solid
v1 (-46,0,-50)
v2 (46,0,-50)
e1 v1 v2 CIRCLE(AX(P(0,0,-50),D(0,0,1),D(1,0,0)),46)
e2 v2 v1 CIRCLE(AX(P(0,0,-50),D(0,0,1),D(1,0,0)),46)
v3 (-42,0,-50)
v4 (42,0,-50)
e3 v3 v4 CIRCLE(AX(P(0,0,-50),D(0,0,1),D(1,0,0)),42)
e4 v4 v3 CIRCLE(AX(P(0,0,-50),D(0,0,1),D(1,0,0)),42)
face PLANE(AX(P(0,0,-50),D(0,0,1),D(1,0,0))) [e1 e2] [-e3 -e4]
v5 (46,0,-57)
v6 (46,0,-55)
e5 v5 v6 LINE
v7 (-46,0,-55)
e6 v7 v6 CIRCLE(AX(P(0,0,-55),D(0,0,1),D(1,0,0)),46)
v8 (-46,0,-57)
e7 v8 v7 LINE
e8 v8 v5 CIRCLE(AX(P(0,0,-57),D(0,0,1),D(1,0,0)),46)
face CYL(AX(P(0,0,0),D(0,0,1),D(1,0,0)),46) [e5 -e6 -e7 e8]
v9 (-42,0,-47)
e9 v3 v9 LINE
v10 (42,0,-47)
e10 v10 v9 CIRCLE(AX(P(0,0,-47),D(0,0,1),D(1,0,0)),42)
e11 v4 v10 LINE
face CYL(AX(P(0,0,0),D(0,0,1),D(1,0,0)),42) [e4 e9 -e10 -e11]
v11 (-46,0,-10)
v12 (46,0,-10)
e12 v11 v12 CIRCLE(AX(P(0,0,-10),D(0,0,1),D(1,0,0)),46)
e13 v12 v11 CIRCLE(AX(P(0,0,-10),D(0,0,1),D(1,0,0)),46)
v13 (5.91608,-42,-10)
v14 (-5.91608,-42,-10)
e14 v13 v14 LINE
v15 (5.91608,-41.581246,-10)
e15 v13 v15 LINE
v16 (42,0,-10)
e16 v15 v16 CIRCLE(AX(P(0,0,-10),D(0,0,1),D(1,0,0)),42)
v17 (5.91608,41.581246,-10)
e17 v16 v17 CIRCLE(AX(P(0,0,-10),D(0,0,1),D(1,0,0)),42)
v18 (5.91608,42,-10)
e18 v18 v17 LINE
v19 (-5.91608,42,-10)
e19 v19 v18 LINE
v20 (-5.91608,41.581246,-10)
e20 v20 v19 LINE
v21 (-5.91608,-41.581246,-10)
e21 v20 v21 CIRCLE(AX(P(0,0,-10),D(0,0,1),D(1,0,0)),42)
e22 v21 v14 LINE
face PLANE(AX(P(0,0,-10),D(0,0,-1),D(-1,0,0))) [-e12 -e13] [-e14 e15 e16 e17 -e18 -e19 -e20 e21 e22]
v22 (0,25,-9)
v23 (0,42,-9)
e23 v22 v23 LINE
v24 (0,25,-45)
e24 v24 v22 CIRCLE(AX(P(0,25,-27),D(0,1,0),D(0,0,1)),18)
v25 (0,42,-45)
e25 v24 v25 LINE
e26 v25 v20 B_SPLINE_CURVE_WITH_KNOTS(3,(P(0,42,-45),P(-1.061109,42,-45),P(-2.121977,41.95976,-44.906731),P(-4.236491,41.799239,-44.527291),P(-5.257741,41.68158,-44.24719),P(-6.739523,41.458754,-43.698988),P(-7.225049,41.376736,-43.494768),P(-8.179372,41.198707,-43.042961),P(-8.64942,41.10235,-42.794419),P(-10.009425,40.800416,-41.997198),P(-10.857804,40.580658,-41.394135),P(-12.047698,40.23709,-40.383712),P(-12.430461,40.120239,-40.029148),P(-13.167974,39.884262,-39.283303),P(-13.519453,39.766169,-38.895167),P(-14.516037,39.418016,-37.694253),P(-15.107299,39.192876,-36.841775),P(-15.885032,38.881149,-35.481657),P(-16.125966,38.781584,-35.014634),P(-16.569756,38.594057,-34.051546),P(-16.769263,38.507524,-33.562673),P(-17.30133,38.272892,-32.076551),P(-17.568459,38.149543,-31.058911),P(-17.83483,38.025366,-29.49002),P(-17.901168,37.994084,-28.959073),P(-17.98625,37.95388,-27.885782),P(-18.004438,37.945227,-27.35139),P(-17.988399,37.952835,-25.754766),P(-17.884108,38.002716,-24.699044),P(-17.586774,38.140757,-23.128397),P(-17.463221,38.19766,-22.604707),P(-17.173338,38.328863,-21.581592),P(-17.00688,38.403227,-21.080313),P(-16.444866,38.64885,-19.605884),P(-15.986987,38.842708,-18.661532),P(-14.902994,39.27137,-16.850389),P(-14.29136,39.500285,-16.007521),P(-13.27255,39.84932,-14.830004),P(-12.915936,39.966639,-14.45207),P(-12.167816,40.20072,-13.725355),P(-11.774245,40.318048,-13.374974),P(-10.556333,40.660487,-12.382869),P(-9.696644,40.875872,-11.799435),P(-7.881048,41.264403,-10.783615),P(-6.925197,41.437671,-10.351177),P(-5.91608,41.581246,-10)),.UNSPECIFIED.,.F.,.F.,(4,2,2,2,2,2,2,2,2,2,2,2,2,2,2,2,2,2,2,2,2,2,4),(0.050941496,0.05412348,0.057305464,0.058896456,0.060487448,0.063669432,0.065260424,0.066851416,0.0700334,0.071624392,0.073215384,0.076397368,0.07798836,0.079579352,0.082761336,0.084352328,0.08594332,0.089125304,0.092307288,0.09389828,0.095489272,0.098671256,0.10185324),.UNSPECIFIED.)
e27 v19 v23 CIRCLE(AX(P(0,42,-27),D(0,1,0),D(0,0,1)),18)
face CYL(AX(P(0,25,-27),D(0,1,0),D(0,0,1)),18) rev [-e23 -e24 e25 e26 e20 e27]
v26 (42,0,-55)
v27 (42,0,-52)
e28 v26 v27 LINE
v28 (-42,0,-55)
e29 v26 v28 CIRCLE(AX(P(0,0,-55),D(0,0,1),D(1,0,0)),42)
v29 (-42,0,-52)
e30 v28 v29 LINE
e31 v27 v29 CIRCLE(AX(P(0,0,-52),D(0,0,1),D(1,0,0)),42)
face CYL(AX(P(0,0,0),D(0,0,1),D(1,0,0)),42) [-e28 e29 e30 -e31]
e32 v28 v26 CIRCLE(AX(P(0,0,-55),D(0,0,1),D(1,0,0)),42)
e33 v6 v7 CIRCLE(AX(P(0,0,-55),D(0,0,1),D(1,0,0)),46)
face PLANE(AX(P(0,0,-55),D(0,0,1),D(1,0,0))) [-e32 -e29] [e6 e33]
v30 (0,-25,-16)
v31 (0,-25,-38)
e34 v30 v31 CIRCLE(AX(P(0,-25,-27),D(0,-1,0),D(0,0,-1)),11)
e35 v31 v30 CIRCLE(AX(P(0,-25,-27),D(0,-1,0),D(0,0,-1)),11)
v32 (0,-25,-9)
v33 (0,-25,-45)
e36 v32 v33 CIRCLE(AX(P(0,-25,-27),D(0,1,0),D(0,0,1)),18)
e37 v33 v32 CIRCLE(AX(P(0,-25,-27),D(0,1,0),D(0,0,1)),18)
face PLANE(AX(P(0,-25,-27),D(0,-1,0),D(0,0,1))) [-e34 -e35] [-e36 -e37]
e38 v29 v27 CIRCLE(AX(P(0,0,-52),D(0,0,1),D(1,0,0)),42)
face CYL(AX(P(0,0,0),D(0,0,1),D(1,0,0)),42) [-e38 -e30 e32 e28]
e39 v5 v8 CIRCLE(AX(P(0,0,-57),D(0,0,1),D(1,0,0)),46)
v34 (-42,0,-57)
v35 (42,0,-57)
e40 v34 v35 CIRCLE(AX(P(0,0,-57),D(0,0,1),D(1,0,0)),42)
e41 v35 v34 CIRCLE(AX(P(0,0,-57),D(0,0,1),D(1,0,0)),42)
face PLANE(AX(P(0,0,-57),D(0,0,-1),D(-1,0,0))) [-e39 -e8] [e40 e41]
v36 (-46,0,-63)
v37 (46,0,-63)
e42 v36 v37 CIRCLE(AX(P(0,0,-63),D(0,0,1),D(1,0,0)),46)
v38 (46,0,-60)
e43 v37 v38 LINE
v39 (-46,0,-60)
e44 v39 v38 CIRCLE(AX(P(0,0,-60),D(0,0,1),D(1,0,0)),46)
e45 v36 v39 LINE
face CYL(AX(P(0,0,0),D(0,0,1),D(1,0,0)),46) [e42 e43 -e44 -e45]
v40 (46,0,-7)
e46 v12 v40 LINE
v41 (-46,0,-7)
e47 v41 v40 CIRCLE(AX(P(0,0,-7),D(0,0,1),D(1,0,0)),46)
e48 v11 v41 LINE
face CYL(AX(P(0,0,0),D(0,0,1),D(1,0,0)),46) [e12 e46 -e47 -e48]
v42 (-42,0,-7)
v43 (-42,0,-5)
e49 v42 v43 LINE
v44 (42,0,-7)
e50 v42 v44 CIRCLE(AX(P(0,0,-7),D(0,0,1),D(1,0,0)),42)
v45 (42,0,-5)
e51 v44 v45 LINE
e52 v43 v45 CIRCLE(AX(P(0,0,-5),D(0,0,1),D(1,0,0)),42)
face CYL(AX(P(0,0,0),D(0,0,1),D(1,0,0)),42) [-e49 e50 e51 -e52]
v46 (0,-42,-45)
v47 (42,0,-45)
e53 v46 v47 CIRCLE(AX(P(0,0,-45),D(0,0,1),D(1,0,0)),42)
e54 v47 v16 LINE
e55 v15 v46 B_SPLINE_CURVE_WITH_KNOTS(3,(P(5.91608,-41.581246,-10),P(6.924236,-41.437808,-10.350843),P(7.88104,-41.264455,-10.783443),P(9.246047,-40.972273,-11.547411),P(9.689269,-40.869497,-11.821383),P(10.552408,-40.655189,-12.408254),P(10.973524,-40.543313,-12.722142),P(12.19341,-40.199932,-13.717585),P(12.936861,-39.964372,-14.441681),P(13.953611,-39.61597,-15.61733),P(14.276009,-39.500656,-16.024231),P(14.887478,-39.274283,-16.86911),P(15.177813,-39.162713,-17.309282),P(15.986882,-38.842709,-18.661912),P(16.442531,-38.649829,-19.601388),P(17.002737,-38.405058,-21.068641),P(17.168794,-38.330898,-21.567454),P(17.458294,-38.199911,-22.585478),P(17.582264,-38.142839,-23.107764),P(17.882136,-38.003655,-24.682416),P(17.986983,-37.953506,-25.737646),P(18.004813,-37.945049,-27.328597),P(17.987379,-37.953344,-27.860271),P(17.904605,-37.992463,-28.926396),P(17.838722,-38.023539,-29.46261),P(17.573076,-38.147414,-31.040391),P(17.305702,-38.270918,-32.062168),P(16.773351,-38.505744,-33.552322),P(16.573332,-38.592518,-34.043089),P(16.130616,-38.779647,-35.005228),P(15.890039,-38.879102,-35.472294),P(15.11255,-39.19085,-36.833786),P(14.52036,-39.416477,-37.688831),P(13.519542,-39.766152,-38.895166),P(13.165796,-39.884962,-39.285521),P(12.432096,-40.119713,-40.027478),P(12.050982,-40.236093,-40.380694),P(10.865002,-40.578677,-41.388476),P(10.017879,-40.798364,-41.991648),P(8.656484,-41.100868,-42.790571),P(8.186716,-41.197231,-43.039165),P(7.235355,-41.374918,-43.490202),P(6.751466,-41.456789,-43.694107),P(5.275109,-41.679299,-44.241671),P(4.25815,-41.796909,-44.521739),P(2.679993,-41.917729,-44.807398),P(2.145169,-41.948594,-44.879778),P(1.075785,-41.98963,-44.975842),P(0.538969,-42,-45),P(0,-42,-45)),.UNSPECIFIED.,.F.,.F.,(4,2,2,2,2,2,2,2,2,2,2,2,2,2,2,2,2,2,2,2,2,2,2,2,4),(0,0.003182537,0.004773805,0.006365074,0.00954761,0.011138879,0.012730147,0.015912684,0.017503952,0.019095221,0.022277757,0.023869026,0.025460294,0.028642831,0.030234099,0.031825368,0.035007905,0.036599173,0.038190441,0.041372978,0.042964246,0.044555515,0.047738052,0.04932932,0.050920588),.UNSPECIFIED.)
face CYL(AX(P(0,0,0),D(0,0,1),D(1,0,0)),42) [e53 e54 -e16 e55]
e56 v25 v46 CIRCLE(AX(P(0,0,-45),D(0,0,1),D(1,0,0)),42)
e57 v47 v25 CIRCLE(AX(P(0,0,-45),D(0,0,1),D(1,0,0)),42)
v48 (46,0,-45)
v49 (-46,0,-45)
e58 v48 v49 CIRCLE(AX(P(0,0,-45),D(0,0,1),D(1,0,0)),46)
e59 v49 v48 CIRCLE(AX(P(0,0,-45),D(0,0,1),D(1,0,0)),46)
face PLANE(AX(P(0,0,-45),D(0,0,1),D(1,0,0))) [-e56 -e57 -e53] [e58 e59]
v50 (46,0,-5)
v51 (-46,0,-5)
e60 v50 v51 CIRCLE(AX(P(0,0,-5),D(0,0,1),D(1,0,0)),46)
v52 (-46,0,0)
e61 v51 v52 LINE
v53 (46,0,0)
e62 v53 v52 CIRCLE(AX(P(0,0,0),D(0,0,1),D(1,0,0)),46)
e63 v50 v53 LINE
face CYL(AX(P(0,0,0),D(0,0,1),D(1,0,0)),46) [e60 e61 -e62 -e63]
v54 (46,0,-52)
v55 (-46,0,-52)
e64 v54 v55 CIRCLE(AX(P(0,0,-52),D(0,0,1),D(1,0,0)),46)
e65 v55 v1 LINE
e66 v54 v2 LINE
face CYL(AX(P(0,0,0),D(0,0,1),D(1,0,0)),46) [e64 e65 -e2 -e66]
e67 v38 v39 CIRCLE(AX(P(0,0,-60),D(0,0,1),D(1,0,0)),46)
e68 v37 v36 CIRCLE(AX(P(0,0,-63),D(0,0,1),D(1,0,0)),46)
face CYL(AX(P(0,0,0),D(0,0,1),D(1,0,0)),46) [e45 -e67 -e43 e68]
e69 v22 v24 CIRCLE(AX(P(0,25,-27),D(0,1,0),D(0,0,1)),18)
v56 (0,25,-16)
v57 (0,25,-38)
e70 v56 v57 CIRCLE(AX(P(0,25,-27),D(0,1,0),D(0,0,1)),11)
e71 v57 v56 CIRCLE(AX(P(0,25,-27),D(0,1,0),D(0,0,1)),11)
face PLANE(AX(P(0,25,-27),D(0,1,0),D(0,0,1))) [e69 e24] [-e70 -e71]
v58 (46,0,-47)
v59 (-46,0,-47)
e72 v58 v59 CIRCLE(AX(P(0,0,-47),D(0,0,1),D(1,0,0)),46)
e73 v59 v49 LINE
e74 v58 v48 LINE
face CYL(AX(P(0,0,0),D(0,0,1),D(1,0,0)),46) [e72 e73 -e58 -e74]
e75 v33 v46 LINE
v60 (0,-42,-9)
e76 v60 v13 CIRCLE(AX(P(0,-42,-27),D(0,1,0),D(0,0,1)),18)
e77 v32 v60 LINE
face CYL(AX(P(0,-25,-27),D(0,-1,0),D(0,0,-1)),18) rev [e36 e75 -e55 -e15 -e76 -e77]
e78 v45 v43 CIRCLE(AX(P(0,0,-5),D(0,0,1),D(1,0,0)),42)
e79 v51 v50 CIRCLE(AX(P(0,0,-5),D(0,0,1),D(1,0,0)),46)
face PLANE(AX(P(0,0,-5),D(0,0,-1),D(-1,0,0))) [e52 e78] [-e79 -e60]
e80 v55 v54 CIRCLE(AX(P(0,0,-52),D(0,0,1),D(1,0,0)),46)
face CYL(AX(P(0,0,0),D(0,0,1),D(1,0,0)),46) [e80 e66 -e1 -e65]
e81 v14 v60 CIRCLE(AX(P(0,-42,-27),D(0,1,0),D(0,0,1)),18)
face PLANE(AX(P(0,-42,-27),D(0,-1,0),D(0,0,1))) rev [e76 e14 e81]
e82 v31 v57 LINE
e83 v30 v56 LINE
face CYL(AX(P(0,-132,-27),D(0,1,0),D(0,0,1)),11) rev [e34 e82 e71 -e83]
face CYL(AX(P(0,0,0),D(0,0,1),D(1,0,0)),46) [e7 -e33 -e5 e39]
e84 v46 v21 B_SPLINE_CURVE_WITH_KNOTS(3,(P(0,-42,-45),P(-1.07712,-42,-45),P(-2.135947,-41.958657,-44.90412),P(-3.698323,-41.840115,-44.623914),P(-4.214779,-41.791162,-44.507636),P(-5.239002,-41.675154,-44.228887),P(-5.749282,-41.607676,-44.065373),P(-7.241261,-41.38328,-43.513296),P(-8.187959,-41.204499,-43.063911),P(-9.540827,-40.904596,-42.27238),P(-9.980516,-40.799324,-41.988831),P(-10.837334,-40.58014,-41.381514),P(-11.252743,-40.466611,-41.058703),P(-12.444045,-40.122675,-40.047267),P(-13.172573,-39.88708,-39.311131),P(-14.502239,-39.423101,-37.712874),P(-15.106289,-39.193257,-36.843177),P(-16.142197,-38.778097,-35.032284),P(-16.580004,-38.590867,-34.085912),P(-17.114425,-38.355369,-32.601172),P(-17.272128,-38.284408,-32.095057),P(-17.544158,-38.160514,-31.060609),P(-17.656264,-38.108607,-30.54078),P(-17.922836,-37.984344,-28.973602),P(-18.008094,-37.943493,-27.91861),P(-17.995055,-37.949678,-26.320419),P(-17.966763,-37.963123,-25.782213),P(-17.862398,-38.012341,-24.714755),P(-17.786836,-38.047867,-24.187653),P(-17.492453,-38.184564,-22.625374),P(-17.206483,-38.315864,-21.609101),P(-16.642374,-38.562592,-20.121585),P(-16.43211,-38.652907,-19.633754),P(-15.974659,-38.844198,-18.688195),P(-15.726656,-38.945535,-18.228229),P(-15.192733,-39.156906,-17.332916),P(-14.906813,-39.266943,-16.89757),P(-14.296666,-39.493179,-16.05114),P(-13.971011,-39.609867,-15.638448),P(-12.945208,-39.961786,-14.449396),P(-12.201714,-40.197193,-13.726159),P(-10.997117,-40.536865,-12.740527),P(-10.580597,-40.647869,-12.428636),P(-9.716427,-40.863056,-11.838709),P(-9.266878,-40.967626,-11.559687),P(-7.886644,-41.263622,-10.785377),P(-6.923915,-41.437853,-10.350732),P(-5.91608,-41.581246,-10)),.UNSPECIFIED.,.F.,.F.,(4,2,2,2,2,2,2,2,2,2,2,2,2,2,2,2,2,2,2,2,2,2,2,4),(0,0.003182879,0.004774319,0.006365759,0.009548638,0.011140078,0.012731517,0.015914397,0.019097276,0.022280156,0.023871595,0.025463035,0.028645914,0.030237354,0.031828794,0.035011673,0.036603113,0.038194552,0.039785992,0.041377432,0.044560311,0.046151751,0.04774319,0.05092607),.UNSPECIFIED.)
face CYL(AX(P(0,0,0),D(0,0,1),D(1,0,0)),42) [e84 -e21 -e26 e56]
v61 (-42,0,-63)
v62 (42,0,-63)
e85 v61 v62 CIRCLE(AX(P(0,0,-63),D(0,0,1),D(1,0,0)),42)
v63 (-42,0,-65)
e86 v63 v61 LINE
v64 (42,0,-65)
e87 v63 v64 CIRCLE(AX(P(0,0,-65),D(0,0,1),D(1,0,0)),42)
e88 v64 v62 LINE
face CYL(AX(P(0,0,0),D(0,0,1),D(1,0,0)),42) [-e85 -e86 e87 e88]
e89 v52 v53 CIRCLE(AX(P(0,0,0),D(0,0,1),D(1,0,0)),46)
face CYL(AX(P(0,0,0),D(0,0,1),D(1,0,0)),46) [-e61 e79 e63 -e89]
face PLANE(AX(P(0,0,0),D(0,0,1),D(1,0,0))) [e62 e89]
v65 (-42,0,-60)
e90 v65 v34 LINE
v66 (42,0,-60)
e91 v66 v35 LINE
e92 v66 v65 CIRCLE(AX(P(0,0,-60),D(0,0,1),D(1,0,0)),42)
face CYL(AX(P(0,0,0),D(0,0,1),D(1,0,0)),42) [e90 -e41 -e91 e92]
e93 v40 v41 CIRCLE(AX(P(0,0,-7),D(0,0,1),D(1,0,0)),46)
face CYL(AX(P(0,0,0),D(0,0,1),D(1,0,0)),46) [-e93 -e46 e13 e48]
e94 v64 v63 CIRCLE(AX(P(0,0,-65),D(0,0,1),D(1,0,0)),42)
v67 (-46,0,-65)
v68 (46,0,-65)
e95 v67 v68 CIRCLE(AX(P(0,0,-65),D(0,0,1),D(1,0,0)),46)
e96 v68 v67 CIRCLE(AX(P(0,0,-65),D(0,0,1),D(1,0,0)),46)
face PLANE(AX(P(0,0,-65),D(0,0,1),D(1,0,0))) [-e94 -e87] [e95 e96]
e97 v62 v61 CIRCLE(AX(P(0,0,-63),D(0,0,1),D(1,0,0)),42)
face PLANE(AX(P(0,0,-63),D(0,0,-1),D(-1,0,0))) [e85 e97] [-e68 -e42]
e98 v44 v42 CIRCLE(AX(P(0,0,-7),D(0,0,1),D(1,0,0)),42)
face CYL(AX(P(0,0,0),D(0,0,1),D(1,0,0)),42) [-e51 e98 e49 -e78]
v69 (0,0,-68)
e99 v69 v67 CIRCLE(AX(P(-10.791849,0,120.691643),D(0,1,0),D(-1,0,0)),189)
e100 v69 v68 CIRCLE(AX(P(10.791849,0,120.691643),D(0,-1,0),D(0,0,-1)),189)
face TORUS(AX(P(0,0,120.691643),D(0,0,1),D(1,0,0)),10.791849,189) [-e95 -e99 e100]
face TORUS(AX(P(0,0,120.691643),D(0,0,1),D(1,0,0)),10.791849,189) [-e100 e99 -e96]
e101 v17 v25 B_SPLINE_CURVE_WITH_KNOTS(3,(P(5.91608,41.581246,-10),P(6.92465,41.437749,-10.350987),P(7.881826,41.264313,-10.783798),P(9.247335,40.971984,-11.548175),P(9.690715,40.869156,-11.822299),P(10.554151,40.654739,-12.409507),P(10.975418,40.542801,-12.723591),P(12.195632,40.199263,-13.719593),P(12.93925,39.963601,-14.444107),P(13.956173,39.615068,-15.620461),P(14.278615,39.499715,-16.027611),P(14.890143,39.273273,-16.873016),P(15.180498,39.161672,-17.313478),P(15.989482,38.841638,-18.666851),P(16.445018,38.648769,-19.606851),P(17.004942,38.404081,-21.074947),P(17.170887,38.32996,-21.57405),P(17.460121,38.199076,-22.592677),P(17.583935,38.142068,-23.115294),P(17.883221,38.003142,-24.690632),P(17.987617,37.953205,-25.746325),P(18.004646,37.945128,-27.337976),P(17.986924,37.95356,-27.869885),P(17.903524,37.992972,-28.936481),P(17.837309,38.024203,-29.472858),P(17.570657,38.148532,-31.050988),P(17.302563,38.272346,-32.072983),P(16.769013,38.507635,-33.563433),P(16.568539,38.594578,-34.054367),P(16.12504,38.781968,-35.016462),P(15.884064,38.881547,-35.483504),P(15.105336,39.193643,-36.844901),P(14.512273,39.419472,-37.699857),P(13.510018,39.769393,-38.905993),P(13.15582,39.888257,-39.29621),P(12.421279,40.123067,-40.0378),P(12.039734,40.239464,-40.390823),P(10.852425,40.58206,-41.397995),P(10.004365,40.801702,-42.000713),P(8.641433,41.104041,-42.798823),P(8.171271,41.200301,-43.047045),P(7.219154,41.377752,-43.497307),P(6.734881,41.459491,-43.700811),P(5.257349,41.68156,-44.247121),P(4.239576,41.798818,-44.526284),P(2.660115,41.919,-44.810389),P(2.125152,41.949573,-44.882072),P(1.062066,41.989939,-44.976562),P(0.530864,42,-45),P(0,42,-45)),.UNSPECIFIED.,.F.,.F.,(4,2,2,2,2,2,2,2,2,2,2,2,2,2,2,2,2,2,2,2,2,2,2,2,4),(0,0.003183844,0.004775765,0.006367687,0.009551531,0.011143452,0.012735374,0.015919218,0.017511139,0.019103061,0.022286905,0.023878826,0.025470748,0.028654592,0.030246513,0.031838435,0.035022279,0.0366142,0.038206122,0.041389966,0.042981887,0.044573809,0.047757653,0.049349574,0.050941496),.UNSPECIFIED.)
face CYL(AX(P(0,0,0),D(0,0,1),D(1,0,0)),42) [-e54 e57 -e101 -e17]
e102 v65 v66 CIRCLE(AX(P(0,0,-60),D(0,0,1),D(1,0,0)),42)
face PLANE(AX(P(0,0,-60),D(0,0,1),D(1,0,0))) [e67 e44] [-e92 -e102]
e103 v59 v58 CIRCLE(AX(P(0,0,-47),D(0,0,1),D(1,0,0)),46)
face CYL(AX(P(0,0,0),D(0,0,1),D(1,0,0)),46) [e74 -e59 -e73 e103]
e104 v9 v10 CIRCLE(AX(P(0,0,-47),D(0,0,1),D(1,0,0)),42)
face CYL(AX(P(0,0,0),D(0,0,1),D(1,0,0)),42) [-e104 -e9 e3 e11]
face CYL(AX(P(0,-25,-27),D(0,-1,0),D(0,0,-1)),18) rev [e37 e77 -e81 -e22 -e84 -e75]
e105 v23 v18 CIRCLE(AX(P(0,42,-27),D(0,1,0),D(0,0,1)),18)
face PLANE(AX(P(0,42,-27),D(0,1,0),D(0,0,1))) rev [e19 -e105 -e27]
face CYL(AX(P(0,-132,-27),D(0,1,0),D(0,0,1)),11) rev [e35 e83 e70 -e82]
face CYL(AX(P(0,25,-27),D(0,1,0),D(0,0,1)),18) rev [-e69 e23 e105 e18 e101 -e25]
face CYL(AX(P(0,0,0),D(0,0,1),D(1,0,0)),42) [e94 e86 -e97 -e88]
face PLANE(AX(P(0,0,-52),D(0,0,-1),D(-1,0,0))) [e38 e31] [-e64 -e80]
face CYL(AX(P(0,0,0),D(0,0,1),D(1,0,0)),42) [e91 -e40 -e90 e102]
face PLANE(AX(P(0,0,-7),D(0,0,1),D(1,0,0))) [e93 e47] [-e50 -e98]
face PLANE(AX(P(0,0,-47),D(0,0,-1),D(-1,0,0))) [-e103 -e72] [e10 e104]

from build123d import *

# Parameters (mm, degrees)
PIN_BOSS_RELIEF_SKETCH_R = 18
PIN_BOSS_RELIEF_36_DEPTH = 17
WRIST_PIN_BORE_SKETCH_R  = 11
WRIST_PIN_BORE_DEPTH     = 157


with BuildPart() as part:
    # Piston Profile Sketch → Piston Body (revolve)
    with BuildSketch(Plane(origin=(0, 0, 0), x_dir=(1, 0, 0), z_dir=(0, 1, 0))):
        with BuildLine():
            ThreePointArc((0, 68), (23.091806354, 67.907697429), (46, 65))
            Line((46, 65), (42, 65))
            Line((42, 65), (42, 63))
            Line((42, 63), (46, 63))
            Line((46, 63), (46, 60))
            Line((46, 60), (42, 60))
            Line((42, 60), (42, 57))
            Line((42, 57), (46, 57))
            Line((46, 57), (46, 55))
            Line((46, 55), (42, 55))
            Line((42, 55), (42, 52))
            Line((42, 52), (46, 52))
            Line((46, 52), (46, 50))
            Line((46, 50), (42, 50))
            Line((42, 50), (42, 47))
            Line((42, 47), (46, 47))
            Line((46, 47), (46, 45))
            Line((46, 45), (42, 45))
            Line((42, 45), (42, 10.377701479))
            Line((42, 10.377701479), (42, 10))
            Line((42, 10), (46, 10))
            Line((46, 10), (46, 7))
            Line((46, 7), (42, 7))
            Line((42, 7), (42, 5))
            Line((42, 5), (46, 5))
            Line((46, 5), (46, 0))
            Line((46, 0), (0, 0))
            Line((0, 0), (0, 68))
        make_face()
    revolve(axis=Axis((0, 0, 0), (0, 0, -1)))

    # Pin Boss Relief Sketch → Pin Boss Relief Ø36 (cut)
    with BuildSketch(Plane(origin=(0, 42, 0), x_dir=(1, 0, 0), z_dir=(0, 1, 0))):
        with Locations(Location((0, 27, 0), (0, 0, 270))):
            Circle(PIN_BOSS_RELIEF_SKETCH_R)
    pin_boss_relief_36 = extrude(amount=-PIN_BOSS_RELIEF_36_DEPTH, mode=Mode.SUBTRACT)

    # Pin Boss Relief Mirror: Pin Boss Relief Ø36 across plane
    add(pin_boss_relief_36.mirror(Plane.ZX), mode=Mode.SUBTRACT)

    # Wrist Pin Bore Sketch → Wrist Pin Bore (cut)
    with BuildSketch(Plane(origin=(0, 25, 0), x_dir=(1, 0, 0), z_dir=(0, 1, 0))):
        with Locations(Location((0, 27, 0), (0, 0, 270))):
            Circle(WRIST_PIN_BORE_SKETCH_R)
    extrude(amount=-WRIST_PIN_BORE_DEPTH, mode=Mode.SUBTRACT)


solid = part.part
